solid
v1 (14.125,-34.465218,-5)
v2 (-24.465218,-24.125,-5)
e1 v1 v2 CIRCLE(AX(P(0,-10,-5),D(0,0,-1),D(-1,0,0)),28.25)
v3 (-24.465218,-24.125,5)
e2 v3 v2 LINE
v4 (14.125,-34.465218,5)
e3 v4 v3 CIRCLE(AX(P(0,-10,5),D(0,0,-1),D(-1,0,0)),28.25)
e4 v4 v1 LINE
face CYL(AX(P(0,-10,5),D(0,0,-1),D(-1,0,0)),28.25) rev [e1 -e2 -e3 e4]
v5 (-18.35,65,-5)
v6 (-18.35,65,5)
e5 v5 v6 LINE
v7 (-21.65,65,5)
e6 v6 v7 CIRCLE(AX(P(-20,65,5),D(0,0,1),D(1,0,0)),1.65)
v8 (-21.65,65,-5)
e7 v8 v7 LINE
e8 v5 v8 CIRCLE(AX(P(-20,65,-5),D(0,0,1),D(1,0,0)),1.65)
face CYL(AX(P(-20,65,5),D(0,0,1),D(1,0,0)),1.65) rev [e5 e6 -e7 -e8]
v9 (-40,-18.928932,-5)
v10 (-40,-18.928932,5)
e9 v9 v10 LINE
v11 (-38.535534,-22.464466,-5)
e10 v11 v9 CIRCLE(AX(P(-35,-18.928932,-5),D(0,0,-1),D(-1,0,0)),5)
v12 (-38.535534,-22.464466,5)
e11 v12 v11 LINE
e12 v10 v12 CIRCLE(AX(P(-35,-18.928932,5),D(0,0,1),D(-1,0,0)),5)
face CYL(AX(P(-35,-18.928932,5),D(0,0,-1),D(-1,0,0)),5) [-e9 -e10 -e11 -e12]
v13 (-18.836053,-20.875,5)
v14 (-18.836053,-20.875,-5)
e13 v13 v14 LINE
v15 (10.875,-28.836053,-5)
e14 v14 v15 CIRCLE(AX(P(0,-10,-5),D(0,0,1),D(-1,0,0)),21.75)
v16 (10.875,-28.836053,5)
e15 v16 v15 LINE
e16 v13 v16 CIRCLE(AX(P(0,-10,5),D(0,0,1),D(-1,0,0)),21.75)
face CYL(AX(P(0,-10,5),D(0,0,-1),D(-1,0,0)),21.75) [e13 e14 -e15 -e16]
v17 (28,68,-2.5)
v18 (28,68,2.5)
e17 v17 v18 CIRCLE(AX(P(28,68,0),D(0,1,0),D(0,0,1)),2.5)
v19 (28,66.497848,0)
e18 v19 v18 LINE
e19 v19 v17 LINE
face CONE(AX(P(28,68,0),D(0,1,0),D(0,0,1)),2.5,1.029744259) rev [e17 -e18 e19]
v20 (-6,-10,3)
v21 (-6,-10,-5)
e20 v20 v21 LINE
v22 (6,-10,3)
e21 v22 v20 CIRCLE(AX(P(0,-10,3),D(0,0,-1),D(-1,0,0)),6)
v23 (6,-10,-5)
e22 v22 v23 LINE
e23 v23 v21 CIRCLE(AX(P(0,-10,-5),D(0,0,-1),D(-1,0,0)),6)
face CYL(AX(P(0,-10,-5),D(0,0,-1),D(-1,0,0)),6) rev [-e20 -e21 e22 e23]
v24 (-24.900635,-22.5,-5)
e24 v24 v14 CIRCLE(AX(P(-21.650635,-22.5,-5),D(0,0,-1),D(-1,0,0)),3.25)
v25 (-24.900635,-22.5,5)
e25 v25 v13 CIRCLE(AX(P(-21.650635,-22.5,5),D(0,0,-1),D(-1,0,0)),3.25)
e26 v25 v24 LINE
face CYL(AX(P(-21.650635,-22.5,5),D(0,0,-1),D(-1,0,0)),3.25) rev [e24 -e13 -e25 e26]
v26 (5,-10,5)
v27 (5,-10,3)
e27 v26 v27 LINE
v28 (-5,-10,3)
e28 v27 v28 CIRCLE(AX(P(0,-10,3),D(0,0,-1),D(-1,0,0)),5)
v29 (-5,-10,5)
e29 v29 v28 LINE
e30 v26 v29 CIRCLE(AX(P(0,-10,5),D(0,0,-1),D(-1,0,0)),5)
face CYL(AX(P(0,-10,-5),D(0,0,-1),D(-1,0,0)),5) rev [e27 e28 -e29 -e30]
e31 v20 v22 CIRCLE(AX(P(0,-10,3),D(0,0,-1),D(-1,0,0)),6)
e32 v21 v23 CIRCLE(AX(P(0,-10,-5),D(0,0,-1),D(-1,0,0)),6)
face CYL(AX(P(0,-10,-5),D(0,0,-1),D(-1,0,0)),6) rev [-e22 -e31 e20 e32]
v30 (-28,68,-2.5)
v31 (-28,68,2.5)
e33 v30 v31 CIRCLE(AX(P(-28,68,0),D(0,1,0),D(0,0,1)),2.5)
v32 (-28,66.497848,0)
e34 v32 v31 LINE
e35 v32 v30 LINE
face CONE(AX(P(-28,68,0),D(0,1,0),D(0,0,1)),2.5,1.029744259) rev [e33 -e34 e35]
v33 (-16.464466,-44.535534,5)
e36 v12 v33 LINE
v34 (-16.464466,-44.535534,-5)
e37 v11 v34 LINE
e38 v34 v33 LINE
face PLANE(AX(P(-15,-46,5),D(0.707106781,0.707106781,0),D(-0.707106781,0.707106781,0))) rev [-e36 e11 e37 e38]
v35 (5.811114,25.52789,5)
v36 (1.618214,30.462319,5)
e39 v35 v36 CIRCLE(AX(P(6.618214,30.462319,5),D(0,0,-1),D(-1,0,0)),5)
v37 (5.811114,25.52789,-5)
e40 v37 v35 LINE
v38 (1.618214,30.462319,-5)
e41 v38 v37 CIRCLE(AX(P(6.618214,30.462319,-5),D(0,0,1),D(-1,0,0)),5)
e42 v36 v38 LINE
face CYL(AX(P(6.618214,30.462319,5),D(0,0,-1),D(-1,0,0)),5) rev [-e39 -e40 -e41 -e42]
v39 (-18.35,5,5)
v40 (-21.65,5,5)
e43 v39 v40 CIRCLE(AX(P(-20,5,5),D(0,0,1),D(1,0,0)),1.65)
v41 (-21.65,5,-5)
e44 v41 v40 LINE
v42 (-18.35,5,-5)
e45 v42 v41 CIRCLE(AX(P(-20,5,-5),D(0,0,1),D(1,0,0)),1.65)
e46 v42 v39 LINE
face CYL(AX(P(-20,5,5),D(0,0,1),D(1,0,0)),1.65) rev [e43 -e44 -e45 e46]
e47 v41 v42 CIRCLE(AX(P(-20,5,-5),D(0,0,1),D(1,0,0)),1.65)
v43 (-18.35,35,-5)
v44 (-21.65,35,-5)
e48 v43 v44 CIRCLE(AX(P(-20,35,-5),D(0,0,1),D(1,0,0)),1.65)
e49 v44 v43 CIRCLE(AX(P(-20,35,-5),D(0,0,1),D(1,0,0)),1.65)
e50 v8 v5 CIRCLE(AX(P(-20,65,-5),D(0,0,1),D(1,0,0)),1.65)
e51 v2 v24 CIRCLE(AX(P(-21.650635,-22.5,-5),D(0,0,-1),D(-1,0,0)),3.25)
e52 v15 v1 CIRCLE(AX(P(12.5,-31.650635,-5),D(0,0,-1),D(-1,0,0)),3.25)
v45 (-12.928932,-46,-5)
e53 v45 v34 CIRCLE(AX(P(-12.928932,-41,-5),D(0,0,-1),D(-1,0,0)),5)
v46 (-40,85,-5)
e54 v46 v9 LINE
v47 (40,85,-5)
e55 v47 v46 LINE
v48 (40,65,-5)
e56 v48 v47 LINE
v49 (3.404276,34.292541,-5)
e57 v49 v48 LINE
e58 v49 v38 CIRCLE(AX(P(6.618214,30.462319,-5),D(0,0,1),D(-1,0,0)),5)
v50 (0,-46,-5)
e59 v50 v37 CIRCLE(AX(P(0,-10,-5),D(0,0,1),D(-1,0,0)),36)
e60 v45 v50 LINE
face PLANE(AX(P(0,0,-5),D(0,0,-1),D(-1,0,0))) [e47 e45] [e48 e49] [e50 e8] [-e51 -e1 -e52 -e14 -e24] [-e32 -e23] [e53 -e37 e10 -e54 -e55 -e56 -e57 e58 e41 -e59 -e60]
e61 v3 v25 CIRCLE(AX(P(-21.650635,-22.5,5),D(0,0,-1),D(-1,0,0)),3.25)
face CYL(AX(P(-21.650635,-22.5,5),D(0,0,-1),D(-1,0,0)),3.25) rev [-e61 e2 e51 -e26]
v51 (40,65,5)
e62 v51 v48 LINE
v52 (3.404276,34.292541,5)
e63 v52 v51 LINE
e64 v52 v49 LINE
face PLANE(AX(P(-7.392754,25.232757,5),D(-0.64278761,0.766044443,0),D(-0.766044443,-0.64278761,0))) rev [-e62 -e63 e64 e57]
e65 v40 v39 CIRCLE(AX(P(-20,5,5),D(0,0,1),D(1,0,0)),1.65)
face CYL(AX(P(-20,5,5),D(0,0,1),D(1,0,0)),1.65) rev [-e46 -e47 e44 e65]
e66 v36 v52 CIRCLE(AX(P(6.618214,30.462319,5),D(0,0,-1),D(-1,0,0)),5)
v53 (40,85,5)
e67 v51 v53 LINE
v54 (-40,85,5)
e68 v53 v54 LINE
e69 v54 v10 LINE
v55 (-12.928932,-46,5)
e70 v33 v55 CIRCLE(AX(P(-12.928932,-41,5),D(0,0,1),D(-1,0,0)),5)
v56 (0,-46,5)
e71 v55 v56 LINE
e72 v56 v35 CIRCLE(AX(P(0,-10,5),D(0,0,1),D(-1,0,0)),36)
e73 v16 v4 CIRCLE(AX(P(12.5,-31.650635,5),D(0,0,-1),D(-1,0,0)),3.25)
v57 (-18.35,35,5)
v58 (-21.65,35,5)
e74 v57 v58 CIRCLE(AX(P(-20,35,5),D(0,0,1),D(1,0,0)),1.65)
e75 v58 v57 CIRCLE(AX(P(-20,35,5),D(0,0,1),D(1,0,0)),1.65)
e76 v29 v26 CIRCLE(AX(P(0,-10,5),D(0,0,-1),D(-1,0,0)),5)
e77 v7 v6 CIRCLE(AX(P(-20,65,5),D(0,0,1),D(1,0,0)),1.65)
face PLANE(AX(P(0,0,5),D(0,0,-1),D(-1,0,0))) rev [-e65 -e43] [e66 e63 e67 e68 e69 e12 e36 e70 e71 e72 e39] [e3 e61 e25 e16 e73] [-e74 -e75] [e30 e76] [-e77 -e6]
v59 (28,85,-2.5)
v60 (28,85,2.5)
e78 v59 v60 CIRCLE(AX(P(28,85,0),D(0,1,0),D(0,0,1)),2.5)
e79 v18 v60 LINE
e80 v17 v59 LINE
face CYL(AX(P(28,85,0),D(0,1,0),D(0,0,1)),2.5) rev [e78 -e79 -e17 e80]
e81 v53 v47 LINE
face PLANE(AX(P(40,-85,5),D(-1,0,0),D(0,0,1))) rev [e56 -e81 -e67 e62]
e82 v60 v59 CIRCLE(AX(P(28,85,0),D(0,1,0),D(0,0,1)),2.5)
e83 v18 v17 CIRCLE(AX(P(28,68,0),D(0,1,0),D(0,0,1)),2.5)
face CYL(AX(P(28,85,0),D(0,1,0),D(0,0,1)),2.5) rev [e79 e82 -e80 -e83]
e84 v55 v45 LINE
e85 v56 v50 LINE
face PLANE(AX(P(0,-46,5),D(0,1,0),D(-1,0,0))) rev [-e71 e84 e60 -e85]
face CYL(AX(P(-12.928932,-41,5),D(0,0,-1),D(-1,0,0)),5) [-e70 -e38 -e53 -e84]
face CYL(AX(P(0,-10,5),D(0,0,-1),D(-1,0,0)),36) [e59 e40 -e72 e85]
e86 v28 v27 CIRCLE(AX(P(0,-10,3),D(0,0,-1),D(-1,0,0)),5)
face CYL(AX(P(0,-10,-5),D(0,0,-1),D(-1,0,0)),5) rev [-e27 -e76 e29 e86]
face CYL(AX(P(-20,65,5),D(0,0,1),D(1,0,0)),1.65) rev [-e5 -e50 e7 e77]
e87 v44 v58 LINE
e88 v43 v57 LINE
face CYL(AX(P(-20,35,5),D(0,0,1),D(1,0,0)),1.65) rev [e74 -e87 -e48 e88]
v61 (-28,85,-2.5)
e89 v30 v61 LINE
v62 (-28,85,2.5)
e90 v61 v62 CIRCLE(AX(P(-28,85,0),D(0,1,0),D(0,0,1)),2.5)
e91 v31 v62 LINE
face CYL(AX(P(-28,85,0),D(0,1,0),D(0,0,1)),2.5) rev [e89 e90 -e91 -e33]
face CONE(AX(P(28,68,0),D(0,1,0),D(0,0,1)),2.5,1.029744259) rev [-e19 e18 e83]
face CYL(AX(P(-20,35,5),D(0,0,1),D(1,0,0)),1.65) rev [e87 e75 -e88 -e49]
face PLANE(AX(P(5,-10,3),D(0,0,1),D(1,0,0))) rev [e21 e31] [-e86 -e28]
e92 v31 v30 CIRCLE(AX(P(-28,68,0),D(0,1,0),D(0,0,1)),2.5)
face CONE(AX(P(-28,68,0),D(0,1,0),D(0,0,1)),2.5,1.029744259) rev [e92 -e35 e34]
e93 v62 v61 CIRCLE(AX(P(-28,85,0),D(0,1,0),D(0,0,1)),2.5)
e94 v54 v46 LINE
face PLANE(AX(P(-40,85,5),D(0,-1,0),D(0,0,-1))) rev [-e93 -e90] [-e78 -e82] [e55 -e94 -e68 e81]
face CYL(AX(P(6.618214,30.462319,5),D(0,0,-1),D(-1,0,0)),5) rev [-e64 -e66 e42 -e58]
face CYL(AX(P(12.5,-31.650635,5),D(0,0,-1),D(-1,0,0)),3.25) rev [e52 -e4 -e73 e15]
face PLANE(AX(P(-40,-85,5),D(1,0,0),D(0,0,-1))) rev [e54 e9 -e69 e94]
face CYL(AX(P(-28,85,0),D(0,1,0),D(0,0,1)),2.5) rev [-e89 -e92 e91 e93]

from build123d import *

# Parameters (mm, degrees)
SKETCH_1_W                = 80
SKETCH_1_H                = 170
EXTRUDE_1_DEPTH           = 5
HOLE_WIZARD_1_D           = 10
HOLE_WIZARD_1_CBORE_D     = 12
HOLE_WIZARD_1_CBORE_DEPTH = 8
CUT_EXTRUDE_2_DEPTH       = 95.472218138
CUT_EXTRUDE_4_DEPTH       = 95.472218138
FILLET_1_R                = 5
HOLE_WIZARD_M6_1_D        = 5
HOLE_WIZARD_M6_1_DEPTH    = 17
HOLE_WIZARD_M6_1_TIP      = 1.502151548
HOLE_WIZARD_M4_1_D        = 3.3


with BuildPart() as part:
    # 草图1 → 凸台-拉伸1 (new, symmetric)
    with BuildSketch(Plane.XY):
        Rectangle(SKETCH_1_W, SKETCH_1_H)
    extrude(amount=EXTRUDE_1_DEPTH, both=True)

    # 孔1 (through all)
    with Locations(Plane(origin=(0, 0, -5), x_dir=(-1, 0, 0), z_dir=(0, 0, -1))):
        with Locations((0, -10)):
            CounterBoreHole(HOLE_WIZARD_1_D / 2, HOLE_WIZARD_1_CBORE_D / 2, HOLE_WIZARD_1_CBORE_DEPTH)

    # 草图6 → 切除-拉伸2 (cut, through all)
    with BuildSketch(Plane(origin=(0, 0, -5), x_dir=(-1, 0, 0), z_dir=(0, 0, -1))):
        with BuildLine():
            ThreePointArc((-14.125, -34.465217657), (7.311638024, -37.287404593), (24.465217657, -24.125))
            ThreePointArc((24.465217657, -24.125), (23.275635095, -19.685417438), (18.836052532, -20.875))
            ThreePointArc((18.836052532, -20.875), (5.629314231, -31.008886722), (-10.875, -28.836052532))
            ThreePointArc((-10.875, -28.836052532), (-15.314582562, -30.025635095), (-14.125, -34.465217657))
        make_face()
    extrude(amount=-CUT_EXTRUDE_2_DEPTH, mode=Mode.SUBTRACT)

    # 草图11 → 切除-拉伸4 (cut, through all)
    with BuildSketch(Plane(origin=(0, 0, -5), x_dir=(-1, 0, 0), z_dir=(0, 0, -1))):
        with BuildLine():
            Line((0, -46), (15, -46))
            Line((15, -46), (40, -21))
            Line((40, -21), (40, -85))
            Line((40, -85), (-40, -85))
            Line((-40, -85), (-40, 65))
            Line((-40, 65), (7.392754444, 25.232757226))
            ThreePointArc((7.392754444, 25.232757226), (-35.807675575, -6.283769392), (0, -46))
        make_face()
    extrude(amount=-CUT_EXTRUDE_4_DEPTH, mode=Mode.SUBTRACT)

    # 圆角1
    fillet_1_edges = [part.edges().sort_by_distance(p)[0] for p in [
        (-40, -21, 0),
        (-7.392754444, 25.232757226, 0),
        (-15, -46, 0),
    ]]
    fillet(fillet_1_edges, radius=FILLET_1_R)

    # M6 螺纹孔1
    with Locations(Plane(origin=(0, 85, 0), x_dir=(1, 0, 0), z_dir=(0, 1, 0))):
        with Locations((-28, 0), (28, 0)):
            Hole(HOLE_WIZARD_M6_1_D / 2, depth=HOLE_WIZARD_M6_1_DEPTH)
            with Locations((0, 0, -(HOLE_WIZARD_M6_1_DEPTH + HOLE_WIZARD_M6_1_TIP / 2))):  # 118° drill point
                Cone(0, HOLE_WIZARD_M6_1_D / 2, HOLE_WIZARD_M6_1_TIP, mode=Mode.SUBTRACT)

    # M4 螺纹孔1 (through all)
    with Locations(Plane.XY.offset(5)):
        with Locations((-20, 65), (-20, 35), (-20, 5)):
            Hole(HOLE_WIZARD_M4_1_D / 2)


solid = part.part
